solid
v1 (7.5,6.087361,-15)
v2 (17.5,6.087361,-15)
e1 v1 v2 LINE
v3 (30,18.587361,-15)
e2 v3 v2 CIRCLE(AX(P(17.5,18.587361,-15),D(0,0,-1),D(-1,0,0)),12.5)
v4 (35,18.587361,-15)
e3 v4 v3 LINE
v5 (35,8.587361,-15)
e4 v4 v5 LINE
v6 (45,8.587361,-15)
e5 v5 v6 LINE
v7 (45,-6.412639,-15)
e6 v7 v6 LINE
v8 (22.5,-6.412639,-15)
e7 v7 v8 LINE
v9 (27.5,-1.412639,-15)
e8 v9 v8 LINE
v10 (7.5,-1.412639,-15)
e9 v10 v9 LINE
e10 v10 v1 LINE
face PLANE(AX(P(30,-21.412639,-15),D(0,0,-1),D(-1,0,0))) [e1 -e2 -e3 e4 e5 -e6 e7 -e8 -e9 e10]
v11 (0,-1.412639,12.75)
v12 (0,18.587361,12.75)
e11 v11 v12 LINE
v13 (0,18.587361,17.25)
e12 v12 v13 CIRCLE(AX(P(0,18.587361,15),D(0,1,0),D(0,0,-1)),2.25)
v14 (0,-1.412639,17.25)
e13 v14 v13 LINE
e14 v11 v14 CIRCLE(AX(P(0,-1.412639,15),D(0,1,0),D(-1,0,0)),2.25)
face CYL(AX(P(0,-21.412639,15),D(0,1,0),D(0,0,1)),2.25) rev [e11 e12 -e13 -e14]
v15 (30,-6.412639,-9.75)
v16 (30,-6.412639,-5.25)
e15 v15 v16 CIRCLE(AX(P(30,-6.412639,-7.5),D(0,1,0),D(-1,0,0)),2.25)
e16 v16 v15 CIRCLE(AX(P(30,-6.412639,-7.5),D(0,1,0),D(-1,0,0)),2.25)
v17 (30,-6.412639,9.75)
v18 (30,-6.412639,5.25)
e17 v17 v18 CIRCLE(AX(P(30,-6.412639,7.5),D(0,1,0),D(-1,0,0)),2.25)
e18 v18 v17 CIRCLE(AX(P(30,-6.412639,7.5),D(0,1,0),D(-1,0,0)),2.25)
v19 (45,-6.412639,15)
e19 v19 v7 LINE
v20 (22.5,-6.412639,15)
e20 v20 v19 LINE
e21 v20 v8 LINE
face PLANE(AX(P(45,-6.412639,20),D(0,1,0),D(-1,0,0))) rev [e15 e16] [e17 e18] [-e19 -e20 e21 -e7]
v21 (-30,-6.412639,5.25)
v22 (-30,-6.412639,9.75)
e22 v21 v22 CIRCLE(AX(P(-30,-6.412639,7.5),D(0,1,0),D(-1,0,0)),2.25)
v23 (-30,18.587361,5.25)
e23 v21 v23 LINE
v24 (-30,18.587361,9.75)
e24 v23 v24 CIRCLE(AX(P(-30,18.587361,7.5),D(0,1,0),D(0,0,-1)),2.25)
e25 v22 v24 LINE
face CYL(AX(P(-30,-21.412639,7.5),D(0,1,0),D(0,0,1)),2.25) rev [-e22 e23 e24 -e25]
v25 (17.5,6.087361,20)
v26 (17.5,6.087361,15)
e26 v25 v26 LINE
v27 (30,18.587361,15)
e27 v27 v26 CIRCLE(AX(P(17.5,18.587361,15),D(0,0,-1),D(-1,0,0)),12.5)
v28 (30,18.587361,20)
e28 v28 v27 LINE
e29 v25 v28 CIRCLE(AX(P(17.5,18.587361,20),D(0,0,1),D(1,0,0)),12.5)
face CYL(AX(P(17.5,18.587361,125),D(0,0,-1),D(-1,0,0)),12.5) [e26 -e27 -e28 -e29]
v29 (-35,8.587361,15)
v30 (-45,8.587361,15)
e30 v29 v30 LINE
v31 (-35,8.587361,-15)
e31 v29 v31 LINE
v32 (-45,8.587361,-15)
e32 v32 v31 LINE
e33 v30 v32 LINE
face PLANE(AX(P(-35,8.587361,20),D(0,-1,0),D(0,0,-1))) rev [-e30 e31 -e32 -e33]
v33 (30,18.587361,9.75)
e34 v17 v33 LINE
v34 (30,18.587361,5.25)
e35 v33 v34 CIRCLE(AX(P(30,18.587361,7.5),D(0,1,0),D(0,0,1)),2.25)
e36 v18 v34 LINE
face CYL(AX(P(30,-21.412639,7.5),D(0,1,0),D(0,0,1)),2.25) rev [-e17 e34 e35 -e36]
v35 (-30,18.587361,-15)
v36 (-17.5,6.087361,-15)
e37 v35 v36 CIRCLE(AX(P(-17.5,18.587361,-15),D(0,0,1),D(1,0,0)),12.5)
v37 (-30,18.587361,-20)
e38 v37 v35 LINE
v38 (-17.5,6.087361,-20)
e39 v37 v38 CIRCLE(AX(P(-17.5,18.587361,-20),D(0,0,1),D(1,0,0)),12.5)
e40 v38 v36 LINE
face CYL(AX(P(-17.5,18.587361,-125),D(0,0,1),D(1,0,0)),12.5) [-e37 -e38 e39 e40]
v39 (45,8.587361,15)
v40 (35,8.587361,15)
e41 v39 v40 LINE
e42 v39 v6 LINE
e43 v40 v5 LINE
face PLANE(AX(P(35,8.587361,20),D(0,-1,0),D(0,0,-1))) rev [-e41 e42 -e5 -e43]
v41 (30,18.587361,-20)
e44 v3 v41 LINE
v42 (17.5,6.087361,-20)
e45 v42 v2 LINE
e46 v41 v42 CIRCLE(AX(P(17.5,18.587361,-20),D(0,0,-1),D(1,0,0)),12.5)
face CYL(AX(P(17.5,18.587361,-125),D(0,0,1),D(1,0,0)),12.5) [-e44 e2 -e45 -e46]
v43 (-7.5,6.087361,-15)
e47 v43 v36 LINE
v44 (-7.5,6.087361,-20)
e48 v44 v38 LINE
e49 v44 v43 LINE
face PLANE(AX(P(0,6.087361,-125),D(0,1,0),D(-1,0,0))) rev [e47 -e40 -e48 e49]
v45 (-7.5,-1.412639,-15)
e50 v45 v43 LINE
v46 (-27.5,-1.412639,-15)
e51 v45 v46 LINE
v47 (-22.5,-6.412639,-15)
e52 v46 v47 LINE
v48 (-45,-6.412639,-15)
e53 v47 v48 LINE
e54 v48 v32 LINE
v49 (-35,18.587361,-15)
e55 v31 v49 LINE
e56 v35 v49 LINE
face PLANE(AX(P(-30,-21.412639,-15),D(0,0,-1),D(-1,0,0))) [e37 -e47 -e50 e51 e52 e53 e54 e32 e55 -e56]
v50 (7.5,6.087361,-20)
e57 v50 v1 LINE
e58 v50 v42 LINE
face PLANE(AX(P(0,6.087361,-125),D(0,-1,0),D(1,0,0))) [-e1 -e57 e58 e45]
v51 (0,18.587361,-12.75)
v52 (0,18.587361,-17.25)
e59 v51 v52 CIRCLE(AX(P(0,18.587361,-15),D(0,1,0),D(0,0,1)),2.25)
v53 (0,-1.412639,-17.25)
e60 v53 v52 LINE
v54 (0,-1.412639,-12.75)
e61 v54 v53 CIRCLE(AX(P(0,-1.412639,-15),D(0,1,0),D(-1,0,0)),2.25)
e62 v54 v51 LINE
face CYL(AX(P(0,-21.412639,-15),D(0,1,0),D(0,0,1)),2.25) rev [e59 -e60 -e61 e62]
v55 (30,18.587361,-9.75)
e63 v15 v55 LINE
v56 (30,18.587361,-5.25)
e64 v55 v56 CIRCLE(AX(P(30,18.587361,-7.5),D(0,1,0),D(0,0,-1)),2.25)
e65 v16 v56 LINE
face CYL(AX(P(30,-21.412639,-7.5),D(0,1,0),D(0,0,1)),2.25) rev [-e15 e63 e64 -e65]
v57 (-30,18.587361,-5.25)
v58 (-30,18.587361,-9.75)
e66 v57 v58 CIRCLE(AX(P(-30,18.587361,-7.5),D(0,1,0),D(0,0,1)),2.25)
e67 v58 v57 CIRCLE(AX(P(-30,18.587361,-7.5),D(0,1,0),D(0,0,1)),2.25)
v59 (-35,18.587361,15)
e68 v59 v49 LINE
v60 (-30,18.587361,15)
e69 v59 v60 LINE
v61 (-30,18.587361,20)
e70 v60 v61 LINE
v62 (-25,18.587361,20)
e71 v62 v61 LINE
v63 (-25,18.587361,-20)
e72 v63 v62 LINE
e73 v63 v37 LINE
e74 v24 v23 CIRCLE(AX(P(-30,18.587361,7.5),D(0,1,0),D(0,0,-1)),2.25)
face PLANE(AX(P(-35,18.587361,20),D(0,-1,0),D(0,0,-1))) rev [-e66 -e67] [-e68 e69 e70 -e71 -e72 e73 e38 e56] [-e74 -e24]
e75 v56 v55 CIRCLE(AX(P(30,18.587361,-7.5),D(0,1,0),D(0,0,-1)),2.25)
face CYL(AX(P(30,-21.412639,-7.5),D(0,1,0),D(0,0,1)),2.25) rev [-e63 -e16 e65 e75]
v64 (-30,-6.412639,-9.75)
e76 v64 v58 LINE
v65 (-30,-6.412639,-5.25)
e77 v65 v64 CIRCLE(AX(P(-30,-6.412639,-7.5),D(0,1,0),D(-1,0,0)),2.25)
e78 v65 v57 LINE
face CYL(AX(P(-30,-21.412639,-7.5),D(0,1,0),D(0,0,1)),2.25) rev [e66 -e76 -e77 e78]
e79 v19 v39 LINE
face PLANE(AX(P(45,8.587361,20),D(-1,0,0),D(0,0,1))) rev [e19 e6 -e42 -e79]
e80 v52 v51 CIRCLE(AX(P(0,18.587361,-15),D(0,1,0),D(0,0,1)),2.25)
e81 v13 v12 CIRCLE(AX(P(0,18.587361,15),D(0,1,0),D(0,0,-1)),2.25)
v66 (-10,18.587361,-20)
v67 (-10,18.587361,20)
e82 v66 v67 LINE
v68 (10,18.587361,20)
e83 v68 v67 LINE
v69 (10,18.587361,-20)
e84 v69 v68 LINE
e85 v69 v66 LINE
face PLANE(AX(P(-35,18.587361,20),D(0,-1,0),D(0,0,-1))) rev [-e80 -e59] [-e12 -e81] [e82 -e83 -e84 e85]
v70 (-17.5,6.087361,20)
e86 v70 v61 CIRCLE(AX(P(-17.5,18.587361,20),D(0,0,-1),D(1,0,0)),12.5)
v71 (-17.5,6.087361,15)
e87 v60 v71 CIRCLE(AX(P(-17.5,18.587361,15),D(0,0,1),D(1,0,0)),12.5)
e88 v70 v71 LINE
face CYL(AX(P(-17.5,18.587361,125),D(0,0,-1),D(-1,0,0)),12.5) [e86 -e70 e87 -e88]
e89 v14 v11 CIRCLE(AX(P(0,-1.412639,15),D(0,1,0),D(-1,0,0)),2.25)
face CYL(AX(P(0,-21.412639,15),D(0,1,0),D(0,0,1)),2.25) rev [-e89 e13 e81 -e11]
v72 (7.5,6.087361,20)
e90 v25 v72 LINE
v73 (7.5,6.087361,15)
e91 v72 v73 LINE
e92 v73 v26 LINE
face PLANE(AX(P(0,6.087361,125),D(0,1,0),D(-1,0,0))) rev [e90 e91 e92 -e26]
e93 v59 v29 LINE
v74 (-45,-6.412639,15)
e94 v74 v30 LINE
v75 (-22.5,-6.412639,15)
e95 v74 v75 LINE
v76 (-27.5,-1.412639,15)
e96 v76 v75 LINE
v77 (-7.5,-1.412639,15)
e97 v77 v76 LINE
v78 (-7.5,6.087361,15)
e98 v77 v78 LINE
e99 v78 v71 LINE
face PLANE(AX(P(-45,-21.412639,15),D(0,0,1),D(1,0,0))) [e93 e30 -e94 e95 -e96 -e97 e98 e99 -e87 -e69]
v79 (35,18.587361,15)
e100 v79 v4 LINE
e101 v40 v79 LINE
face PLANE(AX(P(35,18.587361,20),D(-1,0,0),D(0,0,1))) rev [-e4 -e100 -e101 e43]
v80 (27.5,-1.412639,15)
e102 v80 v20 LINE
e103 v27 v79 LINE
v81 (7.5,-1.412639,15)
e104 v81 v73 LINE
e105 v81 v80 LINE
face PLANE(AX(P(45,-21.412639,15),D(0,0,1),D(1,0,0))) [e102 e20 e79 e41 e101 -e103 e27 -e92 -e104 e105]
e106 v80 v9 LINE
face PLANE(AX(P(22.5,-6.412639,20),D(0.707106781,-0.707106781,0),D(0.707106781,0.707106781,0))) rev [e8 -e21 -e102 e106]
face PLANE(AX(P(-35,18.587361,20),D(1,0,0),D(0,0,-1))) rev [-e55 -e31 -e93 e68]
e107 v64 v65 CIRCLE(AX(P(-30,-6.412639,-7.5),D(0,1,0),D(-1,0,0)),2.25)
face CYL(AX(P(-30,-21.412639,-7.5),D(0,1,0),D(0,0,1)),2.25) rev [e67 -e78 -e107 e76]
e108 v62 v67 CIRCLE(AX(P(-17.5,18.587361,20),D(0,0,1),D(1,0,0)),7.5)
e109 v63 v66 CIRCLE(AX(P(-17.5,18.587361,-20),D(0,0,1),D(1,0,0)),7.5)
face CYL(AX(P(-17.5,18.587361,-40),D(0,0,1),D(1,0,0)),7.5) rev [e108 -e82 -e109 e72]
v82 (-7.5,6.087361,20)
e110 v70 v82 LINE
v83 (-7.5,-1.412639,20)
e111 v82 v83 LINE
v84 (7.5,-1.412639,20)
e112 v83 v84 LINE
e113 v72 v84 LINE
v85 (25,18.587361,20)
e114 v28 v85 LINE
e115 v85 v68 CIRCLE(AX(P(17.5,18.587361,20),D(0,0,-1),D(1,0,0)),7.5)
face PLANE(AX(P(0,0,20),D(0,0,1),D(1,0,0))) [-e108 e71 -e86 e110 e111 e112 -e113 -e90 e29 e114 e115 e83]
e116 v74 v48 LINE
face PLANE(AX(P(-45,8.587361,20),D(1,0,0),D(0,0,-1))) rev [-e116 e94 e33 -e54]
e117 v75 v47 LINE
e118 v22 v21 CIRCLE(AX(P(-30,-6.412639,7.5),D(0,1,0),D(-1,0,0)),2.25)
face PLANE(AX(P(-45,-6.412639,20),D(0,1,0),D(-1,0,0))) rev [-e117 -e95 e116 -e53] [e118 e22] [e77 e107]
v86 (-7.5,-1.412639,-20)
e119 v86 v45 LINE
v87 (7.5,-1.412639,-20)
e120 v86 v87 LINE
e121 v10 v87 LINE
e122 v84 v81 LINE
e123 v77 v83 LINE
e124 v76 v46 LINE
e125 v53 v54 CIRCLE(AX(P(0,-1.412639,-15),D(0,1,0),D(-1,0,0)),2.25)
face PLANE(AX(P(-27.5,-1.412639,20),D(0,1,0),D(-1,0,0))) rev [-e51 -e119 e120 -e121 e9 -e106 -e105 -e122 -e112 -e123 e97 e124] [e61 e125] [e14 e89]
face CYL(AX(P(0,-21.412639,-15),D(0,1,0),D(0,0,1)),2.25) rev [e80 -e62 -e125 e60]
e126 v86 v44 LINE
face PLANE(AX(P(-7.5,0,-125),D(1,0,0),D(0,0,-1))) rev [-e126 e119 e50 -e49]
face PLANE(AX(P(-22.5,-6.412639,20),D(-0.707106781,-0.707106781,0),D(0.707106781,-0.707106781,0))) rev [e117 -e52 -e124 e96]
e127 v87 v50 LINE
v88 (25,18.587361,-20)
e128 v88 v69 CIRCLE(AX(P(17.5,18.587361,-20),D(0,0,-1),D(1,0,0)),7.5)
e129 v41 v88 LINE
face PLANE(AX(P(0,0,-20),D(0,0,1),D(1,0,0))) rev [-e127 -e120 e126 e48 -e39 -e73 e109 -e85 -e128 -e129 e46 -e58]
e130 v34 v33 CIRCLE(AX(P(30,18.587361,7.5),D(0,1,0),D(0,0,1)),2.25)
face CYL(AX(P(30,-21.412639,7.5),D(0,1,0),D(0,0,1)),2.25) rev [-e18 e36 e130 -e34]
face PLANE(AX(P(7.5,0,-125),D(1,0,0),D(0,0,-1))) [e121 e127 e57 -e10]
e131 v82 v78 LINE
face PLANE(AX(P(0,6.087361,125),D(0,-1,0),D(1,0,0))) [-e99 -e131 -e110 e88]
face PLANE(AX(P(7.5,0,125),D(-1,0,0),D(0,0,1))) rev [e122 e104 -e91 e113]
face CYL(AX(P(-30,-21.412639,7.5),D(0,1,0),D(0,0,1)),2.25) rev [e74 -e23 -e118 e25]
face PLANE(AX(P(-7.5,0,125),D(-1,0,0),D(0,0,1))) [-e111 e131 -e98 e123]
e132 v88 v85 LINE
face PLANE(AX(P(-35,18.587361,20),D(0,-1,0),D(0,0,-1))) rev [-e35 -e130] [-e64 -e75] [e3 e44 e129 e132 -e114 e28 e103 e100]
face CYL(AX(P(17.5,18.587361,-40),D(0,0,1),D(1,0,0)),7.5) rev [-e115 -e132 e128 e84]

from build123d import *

# Parameters (mm, degrees)
BASE_BLOCK_DEPTH                 = 20
CENTER_POCKET_SKETCH_OUTSIDE_W   = 112.322
CENTER_POCKET_SKETCH_OUTSIDE_H   = 62.322
CENTER_POCKET_CUT_DEPTH          = 40
MOUNTING_HOLES_SKETCH_R          = 2.25
MOUNTING_HOLES_4_5_DEPTH         = 40
SADDLE_CUT_A_DEPTH               = 55
SADDLE_CUT_B_DEPTH               = 110
SADDLE_MIRROR_RIGHT_COPY_1_DEPTH = 110


with BuildPart() as part:
    # Base Profile Sketch → Base Block (new, symmetric)
    with BuildSketch(Plane.XY):
        Polygon((-35, 18.587360595), (-25, 18.587360595), (-10, 18.587360595), (10, 18.587360595), (25, 18.587360595), (35, 18.587360595), (35, 8.587360595), (45, 8.587360595), (45, -6.412639405), (22.5, -6.412639405), (27.5, -1.412639405), (-27.5, -1.412639405), (-22.5, -6.412639405), (-45, -6.412639405), (-45, 8.587360595), (-35, 8.587360595), align=None)
    extrude(amount=BASE_BLOCK_DEPTH, both=True)

    # Center Pocket Sketch outside → Center Pocket Cut (cut)
    with BuildSketch(Plane(origin=(0, 18.587360595, 0), x_dir=(1, 0, 0), z_dir=(0, 1, 0))):
        Rectangle(CENTER_POCKET_SKETCH_OUTSIDE_W, CENTER_POCKET_SKETCH_OUTSIDE_H)
        Polygon((30, 20), (-30, 20), (-30, 15), (-45, 15), (-45, -15), (-30, -15), (-30, -20), (30, -20), (30, -15), (45, -15), (45, 15), (30, 15), align=None, mode=Mode.SUBTRACT)
    extrude(amount=-CENTER_POCKET_CUT_DEPTH, mode=Mode.SUBTRACT)

    # Mounting Holes Sketch → Mounting Holes _4.5 (cut)
    with BuildSketch(Plane(origin=(0, 18.587360595, 0), x_dir=(1, 0, 0), z_dir=(0, 1, 0))):
        with Locations(Location((-30, 7.5, 0), (0, 0, 270))):
            Circle(MOUNTING_HOLES_SKETCH_R)
        with Locations(Location((-30, -7.5, 0), (0, 0, 180))):
            Circle(MOUNTING_HOLES_SKETCH_R)
        with Locations(Location((30, -7.5, 0), (0, 0, 270))):
            Circle(MOUNTING_HOLES_SKETCH_R)
        with Locations(Location((30, 7.5, 0), (0, 0, 180))):
            Circle(MOUNTING_HOLES_SKETCH_R)
        with Locations(Location((0, 15, 0), (0, 0, 270))):
            Circle(MOUNTING_HOLES_SKETCH_R)
        with Locations(Location((0, -15, 0), (0, 0, 180))):
            Circle(MOUNTING_HOLES_SKETCH_R)
    extrude(amount=-MOUNTING_HOLES_4_5_DEPTH, mode=Mode.SUBTRACT)

    # Saddle Profile Sketch → Saddle Cut A (cut, symmetric)
    with BuildSketch(Plane.XY.offset(15)):
        with BuildLine():
            Line((-10, 18.587360595), (-25, 18.587360595))
            ThreePointArc((-25, 18.587360595), (-17.5, 11.087360595), (-10, 18.587360595))
        make_face()
    saddle_cut_a = extrude(amount=SADDLE_CUT_A_DEPTH, both=True, mode=Mode.SUBTRACT)

    # Sketch5_7 → Saddle Cut B (cut)
    with BuildSketch(Plane.XY.offset(15)):
        with BuildLine():
            ThreePointArc((-17.5, 6.087360595), (-26.338834765, 9.74852583), (-30, 18.587360595))
            Line((-30, 18.587360595), (-30, -6.412639405))
            Line((-30, -6.412639405), (-22.5, -6.412639405))
            Line((-22.5, -6.412639405), (-27.5, -1.412639405))
            Line((-27.5, -1.412639405), (-7.5, -1.412639405))
            Line((-7.5, -1.412639405), (-7.5, 6.087360595))
            Line((-7.5, 6.087360595), (-17.5, 6.087360595))
        make_face()
    saddle_cut_b = extrude(amount=SADDLE_CUT_B_DEPTH, mode=Mode.SUBTRACT)

    # Saddle Mirror Front: Saddle Cut B across plane
    add(saddle_cut_b.mirror(Plane.XY), mode=Mode.SUBTRACT)

    # Saddle Mirror Right: Saddle Cut A, Saddle Cut B across plane
    add(saddle_cut_a.mirror(Plane(origin=(0, 0, 0), x_dir=(0, 0, 1), z_dir=(1, 0, 0))), mode=Mode.SUBTRACT)
    add(saddle_cut_b.mirror(Plane(origin=(0, 0, 0), x_dir=(0, 0, 1), z_dir=(1, 0, 0))), mode=Mode.SUBTRACT)

    # Saddle Mirror Right copy 1 sketch → Saddle Mirror Right copy 1 (cut)
    with BuildSketch(Plane(origin=(0, 0, -15), x_dir=(-1, 0, 0), z_dir=(0, 0, -1))):
        with BuildLine():
            ThreePointArc((-17.5, 6.087360595), (-26.338834765, 9.74852583), (-30, 18.587360595))
            Line((-30, 18.587360595), (-30, -6.412639405))
            Line((-30, -6.412639405), (-22.5, -6.412639405))
            Line((-22.5, -6.412639405), (-27.5, -1.412639405))
            Line((-27.5, -1.412639405), (-7.5, -1.412639405))
            Line((-7.5, -1.412639405), (-7.5, 6.087360595))
            Line((-7.5, 6.087360595), (-17.5, 6.087360595))
        make_face()
    extrude(amount=SADDLE_MIRROR_RIGHT_COPY_1_DEPTH, mode=Mode.SUBTRACT)


solid = part.part
